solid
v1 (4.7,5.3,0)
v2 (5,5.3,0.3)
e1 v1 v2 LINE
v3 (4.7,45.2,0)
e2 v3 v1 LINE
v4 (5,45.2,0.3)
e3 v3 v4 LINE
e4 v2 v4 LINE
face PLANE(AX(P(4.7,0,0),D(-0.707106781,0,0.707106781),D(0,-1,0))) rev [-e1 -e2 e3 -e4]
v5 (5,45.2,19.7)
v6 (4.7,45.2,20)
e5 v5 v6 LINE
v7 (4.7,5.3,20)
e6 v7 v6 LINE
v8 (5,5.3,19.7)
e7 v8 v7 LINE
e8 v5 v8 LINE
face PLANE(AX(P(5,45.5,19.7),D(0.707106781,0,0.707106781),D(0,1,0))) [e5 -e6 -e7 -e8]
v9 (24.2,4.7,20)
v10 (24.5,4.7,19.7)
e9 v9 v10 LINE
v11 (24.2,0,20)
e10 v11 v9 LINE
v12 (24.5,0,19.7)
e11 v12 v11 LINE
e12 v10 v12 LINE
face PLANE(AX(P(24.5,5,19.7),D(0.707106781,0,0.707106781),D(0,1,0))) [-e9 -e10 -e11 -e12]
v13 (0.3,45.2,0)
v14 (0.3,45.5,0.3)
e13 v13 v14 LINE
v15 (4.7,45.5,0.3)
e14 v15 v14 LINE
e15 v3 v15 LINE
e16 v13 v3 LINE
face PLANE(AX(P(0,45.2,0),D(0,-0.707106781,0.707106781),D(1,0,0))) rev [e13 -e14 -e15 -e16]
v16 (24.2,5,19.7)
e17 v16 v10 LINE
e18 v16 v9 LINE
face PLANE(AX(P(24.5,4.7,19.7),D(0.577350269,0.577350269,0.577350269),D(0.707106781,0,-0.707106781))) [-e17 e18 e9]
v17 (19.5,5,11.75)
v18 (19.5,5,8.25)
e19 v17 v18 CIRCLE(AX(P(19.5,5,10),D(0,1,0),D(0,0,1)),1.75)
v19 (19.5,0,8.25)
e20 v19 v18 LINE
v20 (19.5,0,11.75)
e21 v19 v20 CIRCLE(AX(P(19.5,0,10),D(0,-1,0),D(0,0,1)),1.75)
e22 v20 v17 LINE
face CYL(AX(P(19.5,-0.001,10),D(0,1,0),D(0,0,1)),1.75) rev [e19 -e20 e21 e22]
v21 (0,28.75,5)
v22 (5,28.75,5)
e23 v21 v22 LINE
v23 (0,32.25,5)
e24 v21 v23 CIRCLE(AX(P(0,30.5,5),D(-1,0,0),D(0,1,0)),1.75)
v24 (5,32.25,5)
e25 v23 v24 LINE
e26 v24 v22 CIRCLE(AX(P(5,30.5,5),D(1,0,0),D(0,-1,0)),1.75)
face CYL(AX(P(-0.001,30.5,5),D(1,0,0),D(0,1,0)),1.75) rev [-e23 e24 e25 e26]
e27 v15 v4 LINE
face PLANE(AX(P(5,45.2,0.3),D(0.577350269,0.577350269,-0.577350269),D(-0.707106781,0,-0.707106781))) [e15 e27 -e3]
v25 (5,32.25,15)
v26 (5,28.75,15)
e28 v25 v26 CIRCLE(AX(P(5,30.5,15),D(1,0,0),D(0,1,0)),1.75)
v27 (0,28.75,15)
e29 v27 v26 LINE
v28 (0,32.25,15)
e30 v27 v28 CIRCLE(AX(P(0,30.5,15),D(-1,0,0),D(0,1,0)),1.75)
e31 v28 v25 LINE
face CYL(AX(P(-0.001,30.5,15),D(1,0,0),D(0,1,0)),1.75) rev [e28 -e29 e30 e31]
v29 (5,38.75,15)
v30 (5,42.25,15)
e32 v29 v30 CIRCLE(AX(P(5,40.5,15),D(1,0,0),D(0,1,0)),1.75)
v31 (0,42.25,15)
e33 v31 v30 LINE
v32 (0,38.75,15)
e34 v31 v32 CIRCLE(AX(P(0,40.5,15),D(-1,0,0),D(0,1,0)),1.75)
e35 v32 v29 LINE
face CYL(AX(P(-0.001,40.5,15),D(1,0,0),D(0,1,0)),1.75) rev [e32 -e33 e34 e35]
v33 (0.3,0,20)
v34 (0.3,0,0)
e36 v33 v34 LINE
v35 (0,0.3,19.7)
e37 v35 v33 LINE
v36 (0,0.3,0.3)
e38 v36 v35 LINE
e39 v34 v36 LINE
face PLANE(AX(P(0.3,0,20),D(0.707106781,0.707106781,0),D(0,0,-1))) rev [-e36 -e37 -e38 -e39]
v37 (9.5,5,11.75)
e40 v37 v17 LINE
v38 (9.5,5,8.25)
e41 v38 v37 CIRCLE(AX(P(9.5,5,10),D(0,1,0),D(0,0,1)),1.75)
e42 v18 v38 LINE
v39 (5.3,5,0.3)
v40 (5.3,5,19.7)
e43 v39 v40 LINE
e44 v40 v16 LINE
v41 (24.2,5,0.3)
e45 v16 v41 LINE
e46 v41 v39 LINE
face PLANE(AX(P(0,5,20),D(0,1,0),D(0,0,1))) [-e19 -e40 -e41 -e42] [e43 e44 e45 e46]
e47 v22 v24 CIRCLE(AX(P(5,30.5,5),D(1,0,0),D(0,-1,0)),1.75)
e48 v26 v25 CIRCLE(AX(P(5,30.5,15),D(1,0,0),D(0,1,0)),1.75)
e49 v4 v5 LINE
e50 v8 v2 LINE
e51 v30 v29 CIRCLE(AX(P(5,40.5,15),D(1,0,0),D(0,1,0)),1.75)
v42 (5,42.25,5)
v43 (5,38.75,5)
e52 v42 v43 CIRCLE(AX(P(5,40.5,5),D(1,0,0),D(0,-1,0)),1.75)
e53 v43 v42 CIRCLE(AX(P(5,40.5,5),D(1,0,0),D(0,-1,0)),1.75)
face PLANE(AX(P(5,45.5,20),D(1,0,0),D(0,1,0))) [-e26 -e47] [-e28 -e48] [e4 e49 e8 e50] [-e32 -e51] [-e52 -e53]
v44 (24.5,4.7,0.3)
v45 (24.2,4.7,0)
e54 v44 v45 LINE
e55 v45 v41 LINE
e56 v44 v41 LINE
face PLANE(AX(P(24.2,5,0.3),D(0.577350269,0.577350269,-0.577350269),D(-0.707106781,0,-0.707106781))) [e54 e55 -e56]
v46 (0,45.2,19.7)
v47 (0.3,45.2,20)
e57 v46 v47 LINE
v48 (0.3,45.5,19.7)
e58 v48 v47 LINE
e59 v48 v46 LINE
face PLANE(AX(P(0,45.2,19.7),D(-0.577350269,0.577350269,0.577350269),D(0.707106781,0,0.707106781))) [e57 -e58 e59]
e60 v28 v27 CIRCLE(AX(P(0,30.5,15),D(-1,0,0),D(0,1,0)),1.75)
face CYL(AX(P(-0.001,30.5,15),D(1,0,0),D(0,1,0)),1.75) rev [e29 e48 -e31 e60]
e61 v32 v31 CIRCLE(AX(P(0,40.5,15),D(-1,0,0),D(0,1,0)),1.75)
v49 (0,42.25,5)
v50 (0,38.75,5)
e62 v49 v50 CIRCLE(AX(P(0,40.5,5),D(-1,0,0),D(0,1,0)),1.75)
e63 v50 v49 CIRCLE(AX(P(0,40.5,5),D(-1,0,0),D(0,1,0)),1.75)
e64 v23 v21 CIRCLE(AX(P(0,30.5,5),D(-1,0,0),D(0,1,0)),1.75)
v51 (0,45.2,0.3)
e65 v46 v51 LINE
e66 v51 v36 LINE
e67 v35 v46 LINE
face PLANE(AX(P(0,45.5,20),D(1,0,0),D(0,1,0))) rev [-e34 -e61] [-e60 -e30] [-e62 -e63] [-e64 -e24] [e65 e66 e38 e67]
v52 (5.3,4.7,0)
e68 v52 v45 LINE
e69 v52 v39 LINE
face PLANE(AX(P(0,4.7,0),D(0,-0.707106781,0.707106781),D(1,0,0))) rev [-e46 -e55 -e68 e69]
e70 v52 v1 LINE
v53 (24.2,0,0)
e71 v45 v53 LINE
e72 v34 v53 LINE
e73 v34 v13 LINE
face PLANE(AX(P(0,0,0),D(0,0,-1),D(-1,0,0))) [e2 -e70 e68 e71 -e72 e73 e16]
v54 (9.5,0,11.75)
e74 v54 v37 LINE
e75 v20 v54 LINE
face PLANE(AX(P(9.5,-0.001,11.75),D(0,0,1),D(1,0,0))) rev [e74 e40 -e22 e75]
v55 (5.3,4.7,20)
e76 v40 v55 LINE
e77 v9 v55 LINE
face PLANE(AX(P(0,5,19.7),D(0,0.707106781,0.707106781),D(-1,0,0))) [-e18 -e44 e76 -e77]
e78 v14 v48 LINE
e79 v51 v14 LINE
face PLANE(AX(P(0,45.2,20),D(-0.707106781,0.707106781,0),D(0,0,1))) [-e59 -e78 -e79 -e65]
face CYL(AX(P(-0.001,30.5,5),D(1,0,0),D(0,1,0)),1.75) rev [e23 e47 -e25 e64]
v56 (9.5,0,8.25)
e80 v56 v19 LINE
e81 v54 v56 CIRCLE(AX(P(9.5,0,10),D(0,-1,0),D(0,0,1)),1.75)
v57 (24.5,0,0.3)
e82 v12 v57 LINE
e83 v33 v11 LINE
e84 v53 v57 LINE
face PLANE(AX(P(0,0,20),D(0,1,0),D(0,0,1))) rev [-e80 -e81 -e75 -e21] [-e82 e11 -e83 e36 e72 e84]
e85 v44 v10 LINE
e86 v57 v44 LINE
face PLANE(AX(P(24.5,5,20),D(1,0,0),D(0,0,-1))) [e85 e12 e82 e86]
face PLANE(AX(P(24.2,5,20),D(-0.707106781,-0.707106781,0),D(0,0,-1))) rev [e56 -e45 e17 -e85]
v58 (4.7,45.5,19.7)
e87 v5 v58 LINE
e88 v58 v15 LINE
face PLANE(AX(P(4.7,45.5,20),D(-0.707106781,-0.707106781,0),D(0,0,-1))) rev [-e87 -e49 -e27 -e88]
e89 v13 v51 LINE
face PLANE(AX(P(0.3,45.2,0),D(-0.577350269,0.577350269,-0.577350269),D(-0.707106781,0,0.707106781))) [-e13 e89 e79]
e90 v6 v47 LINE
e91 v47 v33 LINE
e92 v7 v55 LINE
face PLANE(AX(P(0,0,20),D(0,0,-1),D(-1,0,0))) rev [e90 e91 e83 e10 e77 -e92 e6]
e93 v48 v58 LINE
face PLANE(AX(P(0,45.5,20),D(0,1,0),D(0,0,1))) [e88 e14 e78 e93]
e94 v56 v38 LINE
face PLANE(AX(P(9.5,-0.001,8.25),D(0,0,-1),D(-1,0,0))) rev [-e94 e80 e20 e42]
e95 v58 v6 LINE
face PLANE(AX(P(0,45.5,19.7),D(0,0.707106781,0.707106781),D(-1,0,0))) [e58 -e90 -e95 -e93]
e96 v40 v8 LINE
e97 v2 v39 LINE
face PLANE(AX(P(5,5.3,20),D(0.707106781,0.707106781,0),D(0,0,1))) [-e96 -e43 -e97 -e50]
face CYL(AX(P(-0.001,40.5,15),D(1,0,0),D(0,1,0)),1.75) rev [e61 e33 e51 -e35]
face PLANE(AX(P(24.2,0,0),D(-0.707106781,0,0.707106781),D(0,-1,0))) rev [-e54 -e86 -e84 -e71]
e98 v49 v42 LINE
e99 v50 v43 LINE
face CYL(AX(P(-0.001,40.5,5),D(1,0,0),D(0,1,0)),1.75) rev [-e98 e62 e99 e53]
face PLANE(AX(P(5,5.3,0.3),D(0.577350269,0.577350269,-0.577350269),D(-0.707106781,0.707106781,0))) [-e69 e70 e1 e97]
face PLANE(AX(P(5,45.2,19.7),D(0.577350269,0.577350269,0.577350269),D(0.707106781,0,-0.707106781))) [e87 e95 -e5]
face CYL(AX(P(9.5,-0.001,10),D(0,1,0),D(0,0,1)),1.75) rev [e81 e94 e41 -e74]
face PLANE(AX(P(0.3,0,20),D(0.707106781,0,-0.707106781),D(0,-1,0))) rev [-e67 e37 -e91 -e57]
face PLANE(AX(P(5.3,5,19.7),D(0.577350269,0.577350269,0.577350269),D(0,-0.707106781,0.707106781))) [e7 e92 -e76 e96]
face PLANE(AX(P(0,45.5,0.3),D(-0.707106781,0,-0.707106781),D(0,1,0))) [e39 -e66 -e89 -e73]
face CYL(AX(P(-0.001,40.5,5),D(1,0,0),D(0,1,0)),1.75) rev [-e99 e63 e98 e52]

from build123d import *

# Parameters (mm, degrees)
EXTRUDE_THIN1_DEPTH = 20
CHAMFER1_SIZE       = 0.3
CUT_EXTRUDE1_REACH  = 53.386
CUT_EXTRUDE2_REACH  = 55.39
SKETCH3_R           = 1.75


with BuildPart() as part:
    # Sketch1 → Extrude-Thin1 (new body)
    with BuildSketch(Plane.XY):
        Polygon((0, 45.5), (0, 0), (24.5, 0), (24.5, 5), (5, 5), (5, 45.5), align=None)
    extrude(amount=EXTRUDE_THIN1_DEPTH)

    # Chamfer1
    chamfer1_edges = [part.edges().sort_by_distance(p)[0] for p in [
        (14.75, 5, 20),
        (5, 25.25, 20),
        (2.5, 45.5, 20),
        (0, 22.75, 20),
        (0, 22.75, 0),
        (2.5, 45.5, 0),
        (5, 25.25, 0),
        (14.75, 5, 0),
        (24.5, 2.5, 0),
        (24.5, 2.5, 20),
        (0, 0, 10),
        (0, 45.5, 10),
        (5, 45.5, 10),
        (5, 5, 10),
        (24.5, 5, 10),
    ]]
    chamfer(chamfer1_edges, length=CHAMFER1_SIZE)

    # Sketch2 → Cut-Extrude1 (cut, up to next)
    with BuildSketch(Plane(origin=(0, 5, 0), x_dir=(1, 0, 0), z_dir=(0, 1, 0)), mode=Mode.PRIVATE) as cut_extrude1_sk1:
        with BuildLine():
            Line((9.5, -8.25), (19.5, -8.25))
            ThreePointArc((19.5, -8.25), (21.25, -10), (19.5, -11.75))
            Line((19.5, -11.75), (9.5, -11.75))
            ThreePointArc((9.5, -11.75), (7.75, -10), (9.5, -8.25))
        make_face()
    cut_extrude1_tool1 = extrude(cut_extrude1_sk1.sketch, amount=-CUT_EXTRUDE1_REACH, mode=Mode.PRIVATE) & part.part
    add(cut_extrude1_tool1.solids().sort_by_distance((14.5, 5, 10))[0], mode=Mode.SUBTRACT)

    # Sketch3 → Cut-Extrude2 (cut, up to next)
    with BuildSketch(Plane(origin=(5, 0, 0), x_dir=(0, 0, -1), z_dir=(1, 0, 0)), mode=Mode.PRIVATE) as cut_extrude2_sk1:
        with Locations(Location((-15, 40.5, 0), (0, 0, 90))):
            Circle(SKETCH3_R)
    cut_extrude2_tool1 = extrude(cut_extrude2_sk1.sketch, amount=-CUT_EXTRUDE2_REACH, mode=Mode.PRIVATE) & part.part
    # Sketch3 → Cut-Extrude2 (cut, up to next)
    with BuildSketch(Plane(origin=(5, 0, 0), x_dir=(0, 0, -1), z_dir=(1, 0, 0)), mode=Mode.PRIVATE) as cut_extrude2_sk2:
        with Locations(Location((-15, 30.5, 0), (0, 0, 90))):
            Circle(SKETCH3_R)
    cut_extrude2_tool2 = extrude(cut_extrude2_sk2.sketch, amount=-CUT_EXTRUDE2_REACH, mode=Mode.PRIVATE) & part.part
    # Sketch3 → Cut-Extrude2 (cut, up to next)
    with BuildSketch(Plane(origin=(5, 0, 0), x_dir=(0, 0, -1), z_dir=(1, 0, 0)), mode=Mode.PRIVATE) as cut_extrude2_sk3:
        with Locations(Location((-5, 30.5, 0), (0, 0, 90))):
            Circle(SKETCH3_R)
    cut_extrude2_tool3 = extrude(cut_extrude2_sk3.sketch, amount=-CUT_EXTRUDE2_REACH, mode=Mode.PRIVATE) & part.part
    # Sketch3 → Cut-Extrude2 (cut, up to next)
    with BuildSketch(Plane(origin=(5, 0, 0), x_dir=(0, 0, -1), z_dir=(1, 0, 0)), mode=Mode.PRIVATE) as cut_extrude2_sk4:
        with Locations(Location((-5, 40.5, 0), (0, 0, 90))):
            Circle(SKETCH3_R)
    cut_extrude2_tool4 = extrude(cut_extrude2_sk4.sketch, amount=-CUT_EXTRUDE2_REACH, mode=Mode.PRIVATE) & part.part
    add(cut_extrude2_tool1.solids().sort_by_distance((5, 40.5, 15))[0], mode=Mode.SUBTRACT)
    add(cut_extrude2_tool2.solids().sort_by_distance((5, 30.5, 15))[0], mode=Mode.SUBTRACT)
    add(cut_extrude2_tool3.solids().sort_by_distance((5, 30.5, 5))[0], mode=Mode.SUBTRACT)
    add(cut_extrude2_tool4.solids().sort_by_distance((5, 40.5, 5))[0], mode=Mode.SUBTRACT)


solid = part.part
